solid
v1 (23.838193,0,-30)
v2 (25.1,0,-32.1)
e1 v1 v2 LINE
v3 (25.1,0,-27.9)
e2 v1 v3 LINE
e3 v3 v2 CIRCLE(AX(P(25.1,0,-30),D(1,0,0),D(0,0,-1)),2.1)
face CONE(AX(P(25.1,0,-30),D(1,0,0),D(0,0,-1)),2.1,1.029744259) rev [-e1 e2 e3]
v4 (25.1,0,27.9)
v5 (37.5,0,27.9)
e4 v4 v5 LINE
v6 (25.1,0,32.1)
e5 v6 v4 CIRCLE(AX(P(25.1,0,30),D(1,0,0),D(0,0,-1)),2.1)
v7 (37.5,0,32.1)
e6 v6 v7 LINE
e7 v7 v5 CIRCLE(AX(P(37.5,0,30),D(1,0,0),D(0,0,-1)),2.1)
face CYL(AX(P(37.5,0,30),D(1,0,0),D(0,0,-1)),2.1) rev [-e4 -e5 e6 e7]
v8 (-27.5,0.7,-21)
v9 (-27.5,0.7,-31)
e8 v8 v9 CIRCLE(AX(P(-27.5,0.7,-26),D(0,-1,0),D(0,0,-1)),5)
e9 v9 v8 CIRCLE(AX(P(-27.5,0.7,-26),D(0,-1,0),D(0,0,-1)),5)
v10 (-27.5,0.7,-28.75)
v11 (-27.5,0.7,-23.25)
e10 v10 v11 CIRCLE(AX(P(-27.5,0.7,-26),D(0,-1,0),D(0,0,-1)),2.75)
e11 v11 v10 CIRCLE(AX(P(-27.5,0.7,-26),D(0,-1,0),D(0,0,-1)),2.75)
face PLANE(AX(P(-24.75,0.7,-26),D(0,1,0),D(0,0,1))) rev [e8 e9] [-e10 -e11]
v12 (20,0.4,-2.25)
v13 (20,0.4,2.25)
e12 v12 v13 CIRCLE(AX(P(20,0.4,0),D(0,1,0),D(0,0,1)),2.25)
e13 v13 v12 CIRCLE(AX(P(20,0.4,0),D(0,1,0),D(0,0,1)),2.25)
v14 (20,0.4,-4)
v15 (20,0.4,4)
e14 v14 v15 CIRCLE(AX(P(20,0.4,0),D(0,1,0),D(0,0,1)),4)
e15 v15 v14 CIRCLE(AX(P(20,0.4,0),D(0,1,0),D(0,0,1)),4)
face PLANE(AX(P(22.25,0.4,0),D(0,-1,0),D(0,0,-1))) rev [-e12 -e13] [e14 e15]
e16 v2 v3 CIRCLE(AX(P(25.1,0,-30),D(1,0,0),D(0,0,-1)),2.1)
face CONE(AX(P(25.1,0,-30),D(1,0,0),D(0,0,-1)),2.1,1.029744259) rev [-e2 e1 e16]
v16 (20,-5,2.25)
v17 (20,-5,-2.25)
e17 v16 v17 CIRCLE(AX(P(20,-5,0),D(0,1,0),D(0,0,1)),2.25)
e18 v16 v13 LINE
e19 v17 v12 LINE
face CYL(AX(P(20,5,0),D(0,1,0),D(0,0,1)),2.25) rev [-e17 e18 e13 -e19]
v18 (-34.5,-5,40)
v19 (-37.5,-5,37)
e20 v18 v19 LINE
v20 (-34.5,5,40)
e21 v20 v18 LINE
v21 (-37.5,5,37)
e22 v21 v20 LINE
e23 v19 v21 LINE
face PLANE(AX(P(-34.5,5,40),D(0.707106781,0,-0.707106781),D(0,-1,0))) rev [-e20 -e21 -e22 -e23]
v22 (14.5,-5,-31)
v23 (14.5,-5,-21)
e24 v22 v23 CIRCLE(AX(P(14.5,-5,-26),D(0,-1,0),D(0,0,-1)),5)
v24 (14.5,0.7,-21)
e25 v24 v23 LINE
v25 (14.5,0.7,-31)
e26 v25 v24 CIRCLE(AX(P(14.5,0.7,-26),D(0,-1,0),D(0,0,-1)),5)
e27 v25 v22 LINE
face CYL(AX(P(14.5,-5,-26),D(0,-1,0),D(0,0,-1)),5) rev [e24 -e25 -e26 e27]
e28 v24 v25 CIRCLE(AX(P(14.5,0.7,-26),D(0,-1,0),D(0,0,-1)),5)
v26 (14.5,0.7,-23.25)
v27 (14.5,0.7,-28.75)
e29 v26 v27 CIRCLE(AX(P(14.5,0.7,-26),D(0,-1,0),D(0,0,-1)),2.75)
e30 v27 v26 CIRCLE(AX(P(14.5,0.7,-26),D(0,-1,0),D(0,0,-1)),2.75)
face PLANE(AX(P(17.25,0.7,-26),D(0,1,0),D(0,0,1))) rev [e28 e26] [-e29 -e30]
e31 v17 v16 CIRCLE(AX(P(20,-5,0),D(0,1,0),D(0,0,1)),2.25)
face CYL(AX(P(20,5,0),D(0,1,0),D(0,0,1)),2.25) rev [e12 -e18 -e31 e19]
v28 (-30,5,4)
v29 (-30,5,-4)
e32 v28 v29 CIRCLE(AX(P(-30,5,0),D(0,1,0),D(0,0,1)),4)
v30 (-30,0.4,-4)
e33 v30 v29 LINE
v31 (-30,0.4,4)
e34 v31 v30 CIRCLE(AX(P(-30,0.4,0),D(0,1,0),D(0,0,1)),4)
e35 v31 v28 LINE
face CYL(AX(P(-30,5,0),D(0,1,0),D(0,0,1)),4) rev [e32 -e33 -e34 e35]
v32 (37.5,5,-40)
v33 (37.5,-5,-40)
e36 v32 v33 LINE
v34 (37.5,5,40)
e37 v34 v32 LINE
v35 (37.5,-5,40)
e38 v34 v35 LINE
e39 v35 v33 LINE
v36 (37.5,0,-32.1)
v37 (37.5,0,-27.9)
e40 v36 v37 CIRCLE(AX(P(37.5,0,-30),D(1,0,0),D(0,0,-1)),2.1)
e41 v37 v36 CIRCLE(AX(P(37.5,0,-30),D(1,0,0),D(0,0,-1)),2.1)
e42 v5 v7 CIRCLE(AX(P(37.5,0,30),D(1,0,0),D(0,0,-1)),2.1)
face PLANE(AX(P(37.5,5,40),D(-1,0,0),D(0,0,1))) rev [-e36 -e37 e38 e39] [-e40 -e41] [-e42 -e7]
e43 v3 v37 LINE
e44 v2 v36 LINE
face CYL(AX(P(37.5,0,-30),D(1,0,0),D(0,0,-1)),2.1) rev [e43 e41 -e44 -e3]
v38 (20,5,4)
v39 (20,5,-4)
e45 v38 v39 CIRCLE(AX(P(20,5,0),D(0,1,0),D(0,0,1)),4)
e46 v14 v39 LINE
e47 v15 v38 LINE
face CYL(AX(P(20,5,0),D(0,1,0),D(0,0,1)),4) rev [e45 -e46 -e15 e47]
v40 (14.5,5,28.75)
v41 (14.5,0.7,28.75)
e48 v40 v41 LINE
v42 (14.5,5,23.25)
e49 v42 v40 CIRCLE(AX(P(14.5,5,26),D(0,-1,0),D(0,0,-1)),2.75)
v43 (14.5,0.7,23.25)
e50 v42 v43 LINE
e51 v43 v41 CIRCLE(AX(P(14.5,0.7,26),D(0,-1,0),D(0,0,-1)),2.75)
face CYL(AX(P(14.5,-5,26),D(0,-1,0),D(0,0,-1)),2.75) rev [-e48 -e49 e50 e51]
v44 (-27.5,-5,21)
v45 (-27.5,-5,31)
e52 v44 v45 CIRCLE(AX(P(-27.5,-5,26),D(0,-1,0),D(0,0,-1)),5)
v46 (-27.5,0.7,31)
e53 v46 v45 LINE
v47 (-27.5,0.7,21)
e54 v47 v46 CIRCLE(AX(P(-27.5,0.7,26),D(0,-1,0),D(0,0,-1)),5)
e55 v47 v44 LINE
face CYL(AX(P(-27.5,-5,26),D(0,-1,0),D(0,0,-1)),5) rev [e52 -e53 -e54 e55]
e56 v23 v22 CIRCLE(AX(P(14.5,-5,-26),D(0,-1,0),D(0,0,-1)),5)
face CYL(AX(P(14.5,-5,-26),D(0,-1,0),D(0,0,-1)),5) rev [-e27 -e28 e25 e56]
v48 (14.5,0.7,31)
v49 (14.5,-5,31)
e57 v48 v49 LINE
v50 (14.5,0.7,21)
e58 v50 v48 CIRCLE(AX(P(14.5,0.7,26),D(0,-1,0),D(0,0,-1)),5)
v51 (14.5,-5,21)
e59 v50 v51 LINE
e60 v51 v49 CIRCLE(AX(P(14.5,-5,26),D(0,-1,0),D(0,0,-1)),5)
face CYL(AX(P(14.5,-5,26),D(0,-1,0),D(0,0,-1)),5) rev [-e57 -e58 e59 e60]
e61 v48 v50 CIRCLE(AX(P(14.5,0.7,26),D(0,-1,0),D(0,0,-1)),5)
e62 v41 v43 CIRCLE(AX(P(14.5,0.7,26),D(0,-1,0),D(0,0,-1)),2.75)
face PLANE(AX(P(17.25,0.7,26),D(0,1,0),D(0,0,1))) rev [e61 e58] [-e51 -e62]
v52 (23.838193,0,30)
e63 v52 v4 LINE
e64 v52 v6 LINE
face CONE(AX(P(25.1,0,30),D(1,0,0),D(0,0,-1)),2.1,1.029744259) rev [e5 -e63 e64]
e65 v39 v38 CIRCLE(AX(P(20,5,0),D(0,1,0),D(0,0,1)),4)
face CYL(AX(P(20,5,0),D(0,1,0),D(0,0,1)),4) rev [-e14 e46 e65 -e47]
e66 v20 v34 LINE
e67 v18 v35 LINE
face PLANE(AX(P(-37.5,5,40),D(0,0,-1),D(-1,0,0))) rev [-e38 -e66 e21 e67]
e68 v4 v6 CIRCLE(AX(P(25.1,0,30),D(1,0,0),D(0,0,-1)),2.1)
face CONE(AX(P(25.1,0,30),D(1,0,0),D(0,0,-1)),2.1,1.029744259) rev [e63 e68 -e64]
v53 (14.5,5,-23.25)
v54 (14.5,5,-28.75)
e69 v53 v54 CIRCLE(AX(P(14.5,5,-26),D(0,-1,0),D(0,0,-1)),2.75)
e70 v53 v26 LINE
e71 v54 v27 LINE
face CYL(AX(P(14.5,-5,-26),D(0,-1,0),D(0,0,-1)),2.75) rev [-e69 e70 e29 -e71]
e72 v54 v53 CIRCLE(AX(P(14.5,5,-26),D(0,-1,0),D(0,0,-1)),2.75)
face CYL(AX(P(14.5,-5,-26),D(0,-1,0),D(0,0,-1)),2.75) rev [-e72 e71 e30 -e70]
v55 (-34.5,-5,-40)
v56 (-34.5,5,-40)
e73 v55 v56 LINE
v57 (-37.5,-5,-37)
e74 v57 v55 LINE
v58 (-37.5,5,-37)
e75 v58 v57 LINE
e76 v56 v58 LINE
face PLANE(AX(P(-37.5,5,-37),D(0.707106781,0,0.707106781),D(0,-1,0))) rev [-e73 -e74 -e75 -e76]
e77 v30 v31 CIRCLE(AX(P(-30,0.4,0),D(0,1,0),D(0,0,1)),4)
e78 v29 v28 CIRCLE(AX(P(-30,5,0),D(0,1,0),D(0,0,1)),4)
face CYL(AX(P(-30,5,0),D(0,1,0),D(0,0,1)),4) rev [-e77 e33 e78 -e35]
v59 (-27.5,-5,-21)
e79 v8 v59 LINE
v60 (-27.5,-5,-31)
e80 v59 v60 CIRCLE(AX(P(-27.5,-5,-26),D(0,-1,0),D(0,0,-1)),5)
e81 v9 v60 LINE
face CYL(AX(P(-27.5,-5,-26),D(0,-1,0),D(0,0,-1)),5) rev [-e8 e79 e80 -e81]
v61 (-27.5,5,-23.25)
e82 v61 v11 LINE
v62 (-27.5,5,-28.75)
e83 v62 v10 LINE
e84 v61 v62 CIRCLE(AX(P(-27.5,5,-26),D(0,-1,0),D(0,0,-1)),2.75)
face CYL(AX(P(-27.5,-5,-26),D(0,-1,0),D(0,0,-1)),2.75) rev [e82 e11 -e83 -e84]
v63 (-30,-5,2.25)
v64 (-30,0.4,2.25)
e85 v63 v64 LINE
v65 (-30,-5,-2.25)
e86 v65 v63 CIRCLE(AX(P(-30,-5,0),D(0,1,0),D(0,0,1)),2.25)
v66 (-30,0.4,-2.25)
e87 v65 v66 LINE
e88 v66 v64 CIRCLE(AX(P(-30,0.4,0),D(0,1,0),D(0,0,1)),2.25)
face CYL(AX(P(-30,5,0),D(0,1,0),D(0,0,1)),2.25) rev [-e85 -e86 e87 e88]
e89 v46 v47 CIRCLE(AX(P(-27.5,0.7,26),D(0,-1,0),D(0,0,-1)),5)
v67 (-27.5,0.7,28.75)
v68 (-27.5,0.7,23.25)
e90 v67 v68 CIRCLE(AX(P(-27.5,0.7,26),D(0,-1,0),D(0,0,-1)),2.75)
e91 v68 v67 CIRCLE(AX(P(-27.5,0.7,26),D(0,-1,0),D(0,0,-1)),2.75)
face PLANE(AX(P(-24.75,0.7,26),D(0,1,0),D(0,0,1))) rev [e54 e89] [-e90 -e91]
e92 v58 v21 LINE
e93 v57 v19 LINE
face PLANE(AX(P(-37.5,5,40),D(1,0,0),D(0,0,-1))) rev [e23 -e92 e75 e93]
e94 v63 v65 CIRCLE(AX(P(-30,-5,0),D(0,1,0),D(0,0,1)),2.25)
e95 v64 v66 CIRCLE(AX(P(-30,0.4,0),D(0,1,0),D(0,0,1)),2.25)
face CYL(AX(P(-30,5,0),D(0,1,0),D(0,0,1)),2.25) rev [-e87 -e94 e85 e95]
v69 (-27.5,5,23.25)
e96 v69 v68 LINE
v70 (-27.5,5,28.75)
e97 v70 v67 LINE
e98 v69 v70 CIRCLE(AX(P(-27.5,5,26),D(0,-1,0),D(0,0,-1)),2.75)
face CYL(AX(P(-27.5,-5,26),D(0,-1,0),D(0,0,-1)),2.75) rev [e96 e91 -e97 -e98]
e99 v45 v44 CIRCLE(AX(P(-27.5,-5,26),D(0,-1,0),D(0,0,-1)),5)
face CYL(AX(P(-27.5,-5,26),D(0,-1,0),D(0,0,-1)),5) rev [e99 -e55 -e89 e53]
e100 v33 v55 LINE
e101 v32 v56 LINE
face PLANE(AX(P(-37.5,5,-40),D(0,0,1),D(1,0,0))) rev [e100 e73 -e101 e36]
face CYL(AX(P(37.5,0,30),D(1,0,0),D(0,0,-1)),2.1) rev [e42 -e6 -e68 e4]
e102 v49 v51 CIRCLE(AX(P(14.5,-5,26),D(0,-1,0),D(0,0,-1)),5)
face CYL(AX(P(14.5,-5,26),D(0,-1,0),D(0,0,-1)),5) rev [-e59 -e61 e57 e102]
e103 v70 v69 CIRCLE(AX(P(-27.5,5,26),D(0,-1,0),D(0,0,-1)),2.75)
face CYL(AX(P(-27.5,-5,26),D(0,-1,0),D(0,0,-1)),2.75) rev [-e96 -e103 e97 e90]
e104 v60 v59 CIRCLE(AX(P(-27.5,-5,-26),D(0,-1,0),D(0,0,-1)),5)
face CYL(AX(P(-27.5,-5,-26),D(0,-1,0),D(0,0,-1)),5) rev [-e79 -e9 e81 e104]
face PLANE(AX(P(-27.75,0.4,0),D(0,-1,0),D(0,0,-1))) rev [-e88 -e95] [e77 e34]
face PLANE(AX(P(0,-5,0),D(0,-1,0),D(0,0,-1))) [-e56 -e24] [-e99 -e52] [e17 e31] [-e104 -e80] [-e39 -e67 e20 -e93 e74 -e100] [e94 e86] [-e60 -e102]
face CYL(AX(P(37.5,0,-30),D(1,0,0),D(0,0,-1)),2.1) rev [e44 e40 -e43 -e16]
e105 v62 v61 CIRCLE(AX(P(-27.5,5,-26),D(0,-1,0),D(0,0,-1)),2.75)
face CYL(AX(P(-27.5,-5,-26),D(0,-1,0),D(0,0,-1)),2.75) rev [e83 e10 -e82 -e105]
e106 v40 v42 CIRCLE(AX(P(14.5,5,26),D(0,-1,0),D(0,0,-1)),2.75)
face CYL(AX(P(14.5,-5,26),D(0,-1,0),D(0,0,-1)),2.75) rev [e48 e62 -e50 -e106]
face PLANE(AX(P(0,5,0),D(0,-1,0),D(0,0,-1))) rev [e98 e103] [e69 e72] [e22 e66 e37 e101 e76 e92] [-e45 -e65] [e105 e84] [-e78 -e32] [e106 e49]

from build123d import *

# Parameters (mm, degrees)
SKETCH_1_W                = 75
SKETCH_1_H                = 80
EXTRUDE_1_DEPTH           = 5
CHAMFER_1_SIZE            = 3
HOLE_WIZARD_M5_1_D        = 4.2
HOLE_WIZARD_M5_1_DEPTH    = 12.4
HOLE_WIZARD_M5_1_TIP      = 1.2618073
HOLE_WIZARD_1_D           = 5.5
HOLE_WIZARD_1_CBORE_D     = 10
HOLE_WIZARD_1_CBORE_DEPTH = 5.7
HOLE_WIZARD_2_D           = 4.5
HOLE_WIZARD_2_CBORE_D     = 8
HOLE_WIZARD_2_CBORE_DEPTH = 4.6


with BuildPart() as part:
    # 草图1 → 凸台-拉伸1 (new, symmetric)
    with BuildSketch(Plane(origin=(0, 0, 0), x_dir=(1, 0, 0), z_dir=(0, 1, 0))):
        Rectangle(SKETCH_1_W, SKETCH_1_H)
    extrude(amount=EXTRUDE_1_DEPTH, both=True)

    # 倒角1
    chamfer_1_edges = [part.edges().sort_by_distance(p)[0] for p in [
        (-37.5, 0, 40),
        (-37.5, 0, -40),
    ]]
    chamfer(chamfer_1_edges, length=CHAMFER_1_SIZE)

    # M5 螺纹孔1
    with Locations(Plane(origin=(37.5, 0, 0), x_dir=(0, 0, -1), z_dir=(1, 0, 0))):
        with Locations((-30, 0), (30, 0)):
            Hole(HOLE_WIZARD_M5_1_D / 2, depth=HOLE_WIZARD_M5_1_DEPTH)
            with Locations((0, 0, -(HOLE_WIZARD_M5_1_DEPTH + HOLE_WIZARD_M5_1_TIP / 2))):  # 118° drill point
                Cone(0, HOLE_WIZARD_M5_1_D / 2, HOLE_WIZARD_M5_1_TIP, mode=Mode.SUBTRACT)

    # 打孔尺寸(%根据)内六角圆柱头螺钉的类型1 (through all)
    with Locations(Plane.XZ.offset(5)):
        with Locations((-27.5, -26), (14.5, -26), (14.5, 26), (-27.5, 26)):
            CounterBoreHole(HOLE_WIZARD_1_D / 2, HOLE_WIZARD_1_CBORE_D / 2, HOLE_WIZARD_1_CBORE_DEPTH)

    # 打孔尺寸(%根据)内六角圆柱头螺钉的类型2 (through all)
    with Locations(Plane(origin=(0, 5, 0), x_dir=(1, 0, 0), z_dir=(0, 1, 0))):
        with Locations((-30, 0), (20, 0)):
            CounterBoreHole(HOLE_WIZARD_2_D / 2, HOLE_WIZARD_2_CBORE_D / 2, HOLE_WIZARD_2_CBORE_DEPTH)


solid = part.part
